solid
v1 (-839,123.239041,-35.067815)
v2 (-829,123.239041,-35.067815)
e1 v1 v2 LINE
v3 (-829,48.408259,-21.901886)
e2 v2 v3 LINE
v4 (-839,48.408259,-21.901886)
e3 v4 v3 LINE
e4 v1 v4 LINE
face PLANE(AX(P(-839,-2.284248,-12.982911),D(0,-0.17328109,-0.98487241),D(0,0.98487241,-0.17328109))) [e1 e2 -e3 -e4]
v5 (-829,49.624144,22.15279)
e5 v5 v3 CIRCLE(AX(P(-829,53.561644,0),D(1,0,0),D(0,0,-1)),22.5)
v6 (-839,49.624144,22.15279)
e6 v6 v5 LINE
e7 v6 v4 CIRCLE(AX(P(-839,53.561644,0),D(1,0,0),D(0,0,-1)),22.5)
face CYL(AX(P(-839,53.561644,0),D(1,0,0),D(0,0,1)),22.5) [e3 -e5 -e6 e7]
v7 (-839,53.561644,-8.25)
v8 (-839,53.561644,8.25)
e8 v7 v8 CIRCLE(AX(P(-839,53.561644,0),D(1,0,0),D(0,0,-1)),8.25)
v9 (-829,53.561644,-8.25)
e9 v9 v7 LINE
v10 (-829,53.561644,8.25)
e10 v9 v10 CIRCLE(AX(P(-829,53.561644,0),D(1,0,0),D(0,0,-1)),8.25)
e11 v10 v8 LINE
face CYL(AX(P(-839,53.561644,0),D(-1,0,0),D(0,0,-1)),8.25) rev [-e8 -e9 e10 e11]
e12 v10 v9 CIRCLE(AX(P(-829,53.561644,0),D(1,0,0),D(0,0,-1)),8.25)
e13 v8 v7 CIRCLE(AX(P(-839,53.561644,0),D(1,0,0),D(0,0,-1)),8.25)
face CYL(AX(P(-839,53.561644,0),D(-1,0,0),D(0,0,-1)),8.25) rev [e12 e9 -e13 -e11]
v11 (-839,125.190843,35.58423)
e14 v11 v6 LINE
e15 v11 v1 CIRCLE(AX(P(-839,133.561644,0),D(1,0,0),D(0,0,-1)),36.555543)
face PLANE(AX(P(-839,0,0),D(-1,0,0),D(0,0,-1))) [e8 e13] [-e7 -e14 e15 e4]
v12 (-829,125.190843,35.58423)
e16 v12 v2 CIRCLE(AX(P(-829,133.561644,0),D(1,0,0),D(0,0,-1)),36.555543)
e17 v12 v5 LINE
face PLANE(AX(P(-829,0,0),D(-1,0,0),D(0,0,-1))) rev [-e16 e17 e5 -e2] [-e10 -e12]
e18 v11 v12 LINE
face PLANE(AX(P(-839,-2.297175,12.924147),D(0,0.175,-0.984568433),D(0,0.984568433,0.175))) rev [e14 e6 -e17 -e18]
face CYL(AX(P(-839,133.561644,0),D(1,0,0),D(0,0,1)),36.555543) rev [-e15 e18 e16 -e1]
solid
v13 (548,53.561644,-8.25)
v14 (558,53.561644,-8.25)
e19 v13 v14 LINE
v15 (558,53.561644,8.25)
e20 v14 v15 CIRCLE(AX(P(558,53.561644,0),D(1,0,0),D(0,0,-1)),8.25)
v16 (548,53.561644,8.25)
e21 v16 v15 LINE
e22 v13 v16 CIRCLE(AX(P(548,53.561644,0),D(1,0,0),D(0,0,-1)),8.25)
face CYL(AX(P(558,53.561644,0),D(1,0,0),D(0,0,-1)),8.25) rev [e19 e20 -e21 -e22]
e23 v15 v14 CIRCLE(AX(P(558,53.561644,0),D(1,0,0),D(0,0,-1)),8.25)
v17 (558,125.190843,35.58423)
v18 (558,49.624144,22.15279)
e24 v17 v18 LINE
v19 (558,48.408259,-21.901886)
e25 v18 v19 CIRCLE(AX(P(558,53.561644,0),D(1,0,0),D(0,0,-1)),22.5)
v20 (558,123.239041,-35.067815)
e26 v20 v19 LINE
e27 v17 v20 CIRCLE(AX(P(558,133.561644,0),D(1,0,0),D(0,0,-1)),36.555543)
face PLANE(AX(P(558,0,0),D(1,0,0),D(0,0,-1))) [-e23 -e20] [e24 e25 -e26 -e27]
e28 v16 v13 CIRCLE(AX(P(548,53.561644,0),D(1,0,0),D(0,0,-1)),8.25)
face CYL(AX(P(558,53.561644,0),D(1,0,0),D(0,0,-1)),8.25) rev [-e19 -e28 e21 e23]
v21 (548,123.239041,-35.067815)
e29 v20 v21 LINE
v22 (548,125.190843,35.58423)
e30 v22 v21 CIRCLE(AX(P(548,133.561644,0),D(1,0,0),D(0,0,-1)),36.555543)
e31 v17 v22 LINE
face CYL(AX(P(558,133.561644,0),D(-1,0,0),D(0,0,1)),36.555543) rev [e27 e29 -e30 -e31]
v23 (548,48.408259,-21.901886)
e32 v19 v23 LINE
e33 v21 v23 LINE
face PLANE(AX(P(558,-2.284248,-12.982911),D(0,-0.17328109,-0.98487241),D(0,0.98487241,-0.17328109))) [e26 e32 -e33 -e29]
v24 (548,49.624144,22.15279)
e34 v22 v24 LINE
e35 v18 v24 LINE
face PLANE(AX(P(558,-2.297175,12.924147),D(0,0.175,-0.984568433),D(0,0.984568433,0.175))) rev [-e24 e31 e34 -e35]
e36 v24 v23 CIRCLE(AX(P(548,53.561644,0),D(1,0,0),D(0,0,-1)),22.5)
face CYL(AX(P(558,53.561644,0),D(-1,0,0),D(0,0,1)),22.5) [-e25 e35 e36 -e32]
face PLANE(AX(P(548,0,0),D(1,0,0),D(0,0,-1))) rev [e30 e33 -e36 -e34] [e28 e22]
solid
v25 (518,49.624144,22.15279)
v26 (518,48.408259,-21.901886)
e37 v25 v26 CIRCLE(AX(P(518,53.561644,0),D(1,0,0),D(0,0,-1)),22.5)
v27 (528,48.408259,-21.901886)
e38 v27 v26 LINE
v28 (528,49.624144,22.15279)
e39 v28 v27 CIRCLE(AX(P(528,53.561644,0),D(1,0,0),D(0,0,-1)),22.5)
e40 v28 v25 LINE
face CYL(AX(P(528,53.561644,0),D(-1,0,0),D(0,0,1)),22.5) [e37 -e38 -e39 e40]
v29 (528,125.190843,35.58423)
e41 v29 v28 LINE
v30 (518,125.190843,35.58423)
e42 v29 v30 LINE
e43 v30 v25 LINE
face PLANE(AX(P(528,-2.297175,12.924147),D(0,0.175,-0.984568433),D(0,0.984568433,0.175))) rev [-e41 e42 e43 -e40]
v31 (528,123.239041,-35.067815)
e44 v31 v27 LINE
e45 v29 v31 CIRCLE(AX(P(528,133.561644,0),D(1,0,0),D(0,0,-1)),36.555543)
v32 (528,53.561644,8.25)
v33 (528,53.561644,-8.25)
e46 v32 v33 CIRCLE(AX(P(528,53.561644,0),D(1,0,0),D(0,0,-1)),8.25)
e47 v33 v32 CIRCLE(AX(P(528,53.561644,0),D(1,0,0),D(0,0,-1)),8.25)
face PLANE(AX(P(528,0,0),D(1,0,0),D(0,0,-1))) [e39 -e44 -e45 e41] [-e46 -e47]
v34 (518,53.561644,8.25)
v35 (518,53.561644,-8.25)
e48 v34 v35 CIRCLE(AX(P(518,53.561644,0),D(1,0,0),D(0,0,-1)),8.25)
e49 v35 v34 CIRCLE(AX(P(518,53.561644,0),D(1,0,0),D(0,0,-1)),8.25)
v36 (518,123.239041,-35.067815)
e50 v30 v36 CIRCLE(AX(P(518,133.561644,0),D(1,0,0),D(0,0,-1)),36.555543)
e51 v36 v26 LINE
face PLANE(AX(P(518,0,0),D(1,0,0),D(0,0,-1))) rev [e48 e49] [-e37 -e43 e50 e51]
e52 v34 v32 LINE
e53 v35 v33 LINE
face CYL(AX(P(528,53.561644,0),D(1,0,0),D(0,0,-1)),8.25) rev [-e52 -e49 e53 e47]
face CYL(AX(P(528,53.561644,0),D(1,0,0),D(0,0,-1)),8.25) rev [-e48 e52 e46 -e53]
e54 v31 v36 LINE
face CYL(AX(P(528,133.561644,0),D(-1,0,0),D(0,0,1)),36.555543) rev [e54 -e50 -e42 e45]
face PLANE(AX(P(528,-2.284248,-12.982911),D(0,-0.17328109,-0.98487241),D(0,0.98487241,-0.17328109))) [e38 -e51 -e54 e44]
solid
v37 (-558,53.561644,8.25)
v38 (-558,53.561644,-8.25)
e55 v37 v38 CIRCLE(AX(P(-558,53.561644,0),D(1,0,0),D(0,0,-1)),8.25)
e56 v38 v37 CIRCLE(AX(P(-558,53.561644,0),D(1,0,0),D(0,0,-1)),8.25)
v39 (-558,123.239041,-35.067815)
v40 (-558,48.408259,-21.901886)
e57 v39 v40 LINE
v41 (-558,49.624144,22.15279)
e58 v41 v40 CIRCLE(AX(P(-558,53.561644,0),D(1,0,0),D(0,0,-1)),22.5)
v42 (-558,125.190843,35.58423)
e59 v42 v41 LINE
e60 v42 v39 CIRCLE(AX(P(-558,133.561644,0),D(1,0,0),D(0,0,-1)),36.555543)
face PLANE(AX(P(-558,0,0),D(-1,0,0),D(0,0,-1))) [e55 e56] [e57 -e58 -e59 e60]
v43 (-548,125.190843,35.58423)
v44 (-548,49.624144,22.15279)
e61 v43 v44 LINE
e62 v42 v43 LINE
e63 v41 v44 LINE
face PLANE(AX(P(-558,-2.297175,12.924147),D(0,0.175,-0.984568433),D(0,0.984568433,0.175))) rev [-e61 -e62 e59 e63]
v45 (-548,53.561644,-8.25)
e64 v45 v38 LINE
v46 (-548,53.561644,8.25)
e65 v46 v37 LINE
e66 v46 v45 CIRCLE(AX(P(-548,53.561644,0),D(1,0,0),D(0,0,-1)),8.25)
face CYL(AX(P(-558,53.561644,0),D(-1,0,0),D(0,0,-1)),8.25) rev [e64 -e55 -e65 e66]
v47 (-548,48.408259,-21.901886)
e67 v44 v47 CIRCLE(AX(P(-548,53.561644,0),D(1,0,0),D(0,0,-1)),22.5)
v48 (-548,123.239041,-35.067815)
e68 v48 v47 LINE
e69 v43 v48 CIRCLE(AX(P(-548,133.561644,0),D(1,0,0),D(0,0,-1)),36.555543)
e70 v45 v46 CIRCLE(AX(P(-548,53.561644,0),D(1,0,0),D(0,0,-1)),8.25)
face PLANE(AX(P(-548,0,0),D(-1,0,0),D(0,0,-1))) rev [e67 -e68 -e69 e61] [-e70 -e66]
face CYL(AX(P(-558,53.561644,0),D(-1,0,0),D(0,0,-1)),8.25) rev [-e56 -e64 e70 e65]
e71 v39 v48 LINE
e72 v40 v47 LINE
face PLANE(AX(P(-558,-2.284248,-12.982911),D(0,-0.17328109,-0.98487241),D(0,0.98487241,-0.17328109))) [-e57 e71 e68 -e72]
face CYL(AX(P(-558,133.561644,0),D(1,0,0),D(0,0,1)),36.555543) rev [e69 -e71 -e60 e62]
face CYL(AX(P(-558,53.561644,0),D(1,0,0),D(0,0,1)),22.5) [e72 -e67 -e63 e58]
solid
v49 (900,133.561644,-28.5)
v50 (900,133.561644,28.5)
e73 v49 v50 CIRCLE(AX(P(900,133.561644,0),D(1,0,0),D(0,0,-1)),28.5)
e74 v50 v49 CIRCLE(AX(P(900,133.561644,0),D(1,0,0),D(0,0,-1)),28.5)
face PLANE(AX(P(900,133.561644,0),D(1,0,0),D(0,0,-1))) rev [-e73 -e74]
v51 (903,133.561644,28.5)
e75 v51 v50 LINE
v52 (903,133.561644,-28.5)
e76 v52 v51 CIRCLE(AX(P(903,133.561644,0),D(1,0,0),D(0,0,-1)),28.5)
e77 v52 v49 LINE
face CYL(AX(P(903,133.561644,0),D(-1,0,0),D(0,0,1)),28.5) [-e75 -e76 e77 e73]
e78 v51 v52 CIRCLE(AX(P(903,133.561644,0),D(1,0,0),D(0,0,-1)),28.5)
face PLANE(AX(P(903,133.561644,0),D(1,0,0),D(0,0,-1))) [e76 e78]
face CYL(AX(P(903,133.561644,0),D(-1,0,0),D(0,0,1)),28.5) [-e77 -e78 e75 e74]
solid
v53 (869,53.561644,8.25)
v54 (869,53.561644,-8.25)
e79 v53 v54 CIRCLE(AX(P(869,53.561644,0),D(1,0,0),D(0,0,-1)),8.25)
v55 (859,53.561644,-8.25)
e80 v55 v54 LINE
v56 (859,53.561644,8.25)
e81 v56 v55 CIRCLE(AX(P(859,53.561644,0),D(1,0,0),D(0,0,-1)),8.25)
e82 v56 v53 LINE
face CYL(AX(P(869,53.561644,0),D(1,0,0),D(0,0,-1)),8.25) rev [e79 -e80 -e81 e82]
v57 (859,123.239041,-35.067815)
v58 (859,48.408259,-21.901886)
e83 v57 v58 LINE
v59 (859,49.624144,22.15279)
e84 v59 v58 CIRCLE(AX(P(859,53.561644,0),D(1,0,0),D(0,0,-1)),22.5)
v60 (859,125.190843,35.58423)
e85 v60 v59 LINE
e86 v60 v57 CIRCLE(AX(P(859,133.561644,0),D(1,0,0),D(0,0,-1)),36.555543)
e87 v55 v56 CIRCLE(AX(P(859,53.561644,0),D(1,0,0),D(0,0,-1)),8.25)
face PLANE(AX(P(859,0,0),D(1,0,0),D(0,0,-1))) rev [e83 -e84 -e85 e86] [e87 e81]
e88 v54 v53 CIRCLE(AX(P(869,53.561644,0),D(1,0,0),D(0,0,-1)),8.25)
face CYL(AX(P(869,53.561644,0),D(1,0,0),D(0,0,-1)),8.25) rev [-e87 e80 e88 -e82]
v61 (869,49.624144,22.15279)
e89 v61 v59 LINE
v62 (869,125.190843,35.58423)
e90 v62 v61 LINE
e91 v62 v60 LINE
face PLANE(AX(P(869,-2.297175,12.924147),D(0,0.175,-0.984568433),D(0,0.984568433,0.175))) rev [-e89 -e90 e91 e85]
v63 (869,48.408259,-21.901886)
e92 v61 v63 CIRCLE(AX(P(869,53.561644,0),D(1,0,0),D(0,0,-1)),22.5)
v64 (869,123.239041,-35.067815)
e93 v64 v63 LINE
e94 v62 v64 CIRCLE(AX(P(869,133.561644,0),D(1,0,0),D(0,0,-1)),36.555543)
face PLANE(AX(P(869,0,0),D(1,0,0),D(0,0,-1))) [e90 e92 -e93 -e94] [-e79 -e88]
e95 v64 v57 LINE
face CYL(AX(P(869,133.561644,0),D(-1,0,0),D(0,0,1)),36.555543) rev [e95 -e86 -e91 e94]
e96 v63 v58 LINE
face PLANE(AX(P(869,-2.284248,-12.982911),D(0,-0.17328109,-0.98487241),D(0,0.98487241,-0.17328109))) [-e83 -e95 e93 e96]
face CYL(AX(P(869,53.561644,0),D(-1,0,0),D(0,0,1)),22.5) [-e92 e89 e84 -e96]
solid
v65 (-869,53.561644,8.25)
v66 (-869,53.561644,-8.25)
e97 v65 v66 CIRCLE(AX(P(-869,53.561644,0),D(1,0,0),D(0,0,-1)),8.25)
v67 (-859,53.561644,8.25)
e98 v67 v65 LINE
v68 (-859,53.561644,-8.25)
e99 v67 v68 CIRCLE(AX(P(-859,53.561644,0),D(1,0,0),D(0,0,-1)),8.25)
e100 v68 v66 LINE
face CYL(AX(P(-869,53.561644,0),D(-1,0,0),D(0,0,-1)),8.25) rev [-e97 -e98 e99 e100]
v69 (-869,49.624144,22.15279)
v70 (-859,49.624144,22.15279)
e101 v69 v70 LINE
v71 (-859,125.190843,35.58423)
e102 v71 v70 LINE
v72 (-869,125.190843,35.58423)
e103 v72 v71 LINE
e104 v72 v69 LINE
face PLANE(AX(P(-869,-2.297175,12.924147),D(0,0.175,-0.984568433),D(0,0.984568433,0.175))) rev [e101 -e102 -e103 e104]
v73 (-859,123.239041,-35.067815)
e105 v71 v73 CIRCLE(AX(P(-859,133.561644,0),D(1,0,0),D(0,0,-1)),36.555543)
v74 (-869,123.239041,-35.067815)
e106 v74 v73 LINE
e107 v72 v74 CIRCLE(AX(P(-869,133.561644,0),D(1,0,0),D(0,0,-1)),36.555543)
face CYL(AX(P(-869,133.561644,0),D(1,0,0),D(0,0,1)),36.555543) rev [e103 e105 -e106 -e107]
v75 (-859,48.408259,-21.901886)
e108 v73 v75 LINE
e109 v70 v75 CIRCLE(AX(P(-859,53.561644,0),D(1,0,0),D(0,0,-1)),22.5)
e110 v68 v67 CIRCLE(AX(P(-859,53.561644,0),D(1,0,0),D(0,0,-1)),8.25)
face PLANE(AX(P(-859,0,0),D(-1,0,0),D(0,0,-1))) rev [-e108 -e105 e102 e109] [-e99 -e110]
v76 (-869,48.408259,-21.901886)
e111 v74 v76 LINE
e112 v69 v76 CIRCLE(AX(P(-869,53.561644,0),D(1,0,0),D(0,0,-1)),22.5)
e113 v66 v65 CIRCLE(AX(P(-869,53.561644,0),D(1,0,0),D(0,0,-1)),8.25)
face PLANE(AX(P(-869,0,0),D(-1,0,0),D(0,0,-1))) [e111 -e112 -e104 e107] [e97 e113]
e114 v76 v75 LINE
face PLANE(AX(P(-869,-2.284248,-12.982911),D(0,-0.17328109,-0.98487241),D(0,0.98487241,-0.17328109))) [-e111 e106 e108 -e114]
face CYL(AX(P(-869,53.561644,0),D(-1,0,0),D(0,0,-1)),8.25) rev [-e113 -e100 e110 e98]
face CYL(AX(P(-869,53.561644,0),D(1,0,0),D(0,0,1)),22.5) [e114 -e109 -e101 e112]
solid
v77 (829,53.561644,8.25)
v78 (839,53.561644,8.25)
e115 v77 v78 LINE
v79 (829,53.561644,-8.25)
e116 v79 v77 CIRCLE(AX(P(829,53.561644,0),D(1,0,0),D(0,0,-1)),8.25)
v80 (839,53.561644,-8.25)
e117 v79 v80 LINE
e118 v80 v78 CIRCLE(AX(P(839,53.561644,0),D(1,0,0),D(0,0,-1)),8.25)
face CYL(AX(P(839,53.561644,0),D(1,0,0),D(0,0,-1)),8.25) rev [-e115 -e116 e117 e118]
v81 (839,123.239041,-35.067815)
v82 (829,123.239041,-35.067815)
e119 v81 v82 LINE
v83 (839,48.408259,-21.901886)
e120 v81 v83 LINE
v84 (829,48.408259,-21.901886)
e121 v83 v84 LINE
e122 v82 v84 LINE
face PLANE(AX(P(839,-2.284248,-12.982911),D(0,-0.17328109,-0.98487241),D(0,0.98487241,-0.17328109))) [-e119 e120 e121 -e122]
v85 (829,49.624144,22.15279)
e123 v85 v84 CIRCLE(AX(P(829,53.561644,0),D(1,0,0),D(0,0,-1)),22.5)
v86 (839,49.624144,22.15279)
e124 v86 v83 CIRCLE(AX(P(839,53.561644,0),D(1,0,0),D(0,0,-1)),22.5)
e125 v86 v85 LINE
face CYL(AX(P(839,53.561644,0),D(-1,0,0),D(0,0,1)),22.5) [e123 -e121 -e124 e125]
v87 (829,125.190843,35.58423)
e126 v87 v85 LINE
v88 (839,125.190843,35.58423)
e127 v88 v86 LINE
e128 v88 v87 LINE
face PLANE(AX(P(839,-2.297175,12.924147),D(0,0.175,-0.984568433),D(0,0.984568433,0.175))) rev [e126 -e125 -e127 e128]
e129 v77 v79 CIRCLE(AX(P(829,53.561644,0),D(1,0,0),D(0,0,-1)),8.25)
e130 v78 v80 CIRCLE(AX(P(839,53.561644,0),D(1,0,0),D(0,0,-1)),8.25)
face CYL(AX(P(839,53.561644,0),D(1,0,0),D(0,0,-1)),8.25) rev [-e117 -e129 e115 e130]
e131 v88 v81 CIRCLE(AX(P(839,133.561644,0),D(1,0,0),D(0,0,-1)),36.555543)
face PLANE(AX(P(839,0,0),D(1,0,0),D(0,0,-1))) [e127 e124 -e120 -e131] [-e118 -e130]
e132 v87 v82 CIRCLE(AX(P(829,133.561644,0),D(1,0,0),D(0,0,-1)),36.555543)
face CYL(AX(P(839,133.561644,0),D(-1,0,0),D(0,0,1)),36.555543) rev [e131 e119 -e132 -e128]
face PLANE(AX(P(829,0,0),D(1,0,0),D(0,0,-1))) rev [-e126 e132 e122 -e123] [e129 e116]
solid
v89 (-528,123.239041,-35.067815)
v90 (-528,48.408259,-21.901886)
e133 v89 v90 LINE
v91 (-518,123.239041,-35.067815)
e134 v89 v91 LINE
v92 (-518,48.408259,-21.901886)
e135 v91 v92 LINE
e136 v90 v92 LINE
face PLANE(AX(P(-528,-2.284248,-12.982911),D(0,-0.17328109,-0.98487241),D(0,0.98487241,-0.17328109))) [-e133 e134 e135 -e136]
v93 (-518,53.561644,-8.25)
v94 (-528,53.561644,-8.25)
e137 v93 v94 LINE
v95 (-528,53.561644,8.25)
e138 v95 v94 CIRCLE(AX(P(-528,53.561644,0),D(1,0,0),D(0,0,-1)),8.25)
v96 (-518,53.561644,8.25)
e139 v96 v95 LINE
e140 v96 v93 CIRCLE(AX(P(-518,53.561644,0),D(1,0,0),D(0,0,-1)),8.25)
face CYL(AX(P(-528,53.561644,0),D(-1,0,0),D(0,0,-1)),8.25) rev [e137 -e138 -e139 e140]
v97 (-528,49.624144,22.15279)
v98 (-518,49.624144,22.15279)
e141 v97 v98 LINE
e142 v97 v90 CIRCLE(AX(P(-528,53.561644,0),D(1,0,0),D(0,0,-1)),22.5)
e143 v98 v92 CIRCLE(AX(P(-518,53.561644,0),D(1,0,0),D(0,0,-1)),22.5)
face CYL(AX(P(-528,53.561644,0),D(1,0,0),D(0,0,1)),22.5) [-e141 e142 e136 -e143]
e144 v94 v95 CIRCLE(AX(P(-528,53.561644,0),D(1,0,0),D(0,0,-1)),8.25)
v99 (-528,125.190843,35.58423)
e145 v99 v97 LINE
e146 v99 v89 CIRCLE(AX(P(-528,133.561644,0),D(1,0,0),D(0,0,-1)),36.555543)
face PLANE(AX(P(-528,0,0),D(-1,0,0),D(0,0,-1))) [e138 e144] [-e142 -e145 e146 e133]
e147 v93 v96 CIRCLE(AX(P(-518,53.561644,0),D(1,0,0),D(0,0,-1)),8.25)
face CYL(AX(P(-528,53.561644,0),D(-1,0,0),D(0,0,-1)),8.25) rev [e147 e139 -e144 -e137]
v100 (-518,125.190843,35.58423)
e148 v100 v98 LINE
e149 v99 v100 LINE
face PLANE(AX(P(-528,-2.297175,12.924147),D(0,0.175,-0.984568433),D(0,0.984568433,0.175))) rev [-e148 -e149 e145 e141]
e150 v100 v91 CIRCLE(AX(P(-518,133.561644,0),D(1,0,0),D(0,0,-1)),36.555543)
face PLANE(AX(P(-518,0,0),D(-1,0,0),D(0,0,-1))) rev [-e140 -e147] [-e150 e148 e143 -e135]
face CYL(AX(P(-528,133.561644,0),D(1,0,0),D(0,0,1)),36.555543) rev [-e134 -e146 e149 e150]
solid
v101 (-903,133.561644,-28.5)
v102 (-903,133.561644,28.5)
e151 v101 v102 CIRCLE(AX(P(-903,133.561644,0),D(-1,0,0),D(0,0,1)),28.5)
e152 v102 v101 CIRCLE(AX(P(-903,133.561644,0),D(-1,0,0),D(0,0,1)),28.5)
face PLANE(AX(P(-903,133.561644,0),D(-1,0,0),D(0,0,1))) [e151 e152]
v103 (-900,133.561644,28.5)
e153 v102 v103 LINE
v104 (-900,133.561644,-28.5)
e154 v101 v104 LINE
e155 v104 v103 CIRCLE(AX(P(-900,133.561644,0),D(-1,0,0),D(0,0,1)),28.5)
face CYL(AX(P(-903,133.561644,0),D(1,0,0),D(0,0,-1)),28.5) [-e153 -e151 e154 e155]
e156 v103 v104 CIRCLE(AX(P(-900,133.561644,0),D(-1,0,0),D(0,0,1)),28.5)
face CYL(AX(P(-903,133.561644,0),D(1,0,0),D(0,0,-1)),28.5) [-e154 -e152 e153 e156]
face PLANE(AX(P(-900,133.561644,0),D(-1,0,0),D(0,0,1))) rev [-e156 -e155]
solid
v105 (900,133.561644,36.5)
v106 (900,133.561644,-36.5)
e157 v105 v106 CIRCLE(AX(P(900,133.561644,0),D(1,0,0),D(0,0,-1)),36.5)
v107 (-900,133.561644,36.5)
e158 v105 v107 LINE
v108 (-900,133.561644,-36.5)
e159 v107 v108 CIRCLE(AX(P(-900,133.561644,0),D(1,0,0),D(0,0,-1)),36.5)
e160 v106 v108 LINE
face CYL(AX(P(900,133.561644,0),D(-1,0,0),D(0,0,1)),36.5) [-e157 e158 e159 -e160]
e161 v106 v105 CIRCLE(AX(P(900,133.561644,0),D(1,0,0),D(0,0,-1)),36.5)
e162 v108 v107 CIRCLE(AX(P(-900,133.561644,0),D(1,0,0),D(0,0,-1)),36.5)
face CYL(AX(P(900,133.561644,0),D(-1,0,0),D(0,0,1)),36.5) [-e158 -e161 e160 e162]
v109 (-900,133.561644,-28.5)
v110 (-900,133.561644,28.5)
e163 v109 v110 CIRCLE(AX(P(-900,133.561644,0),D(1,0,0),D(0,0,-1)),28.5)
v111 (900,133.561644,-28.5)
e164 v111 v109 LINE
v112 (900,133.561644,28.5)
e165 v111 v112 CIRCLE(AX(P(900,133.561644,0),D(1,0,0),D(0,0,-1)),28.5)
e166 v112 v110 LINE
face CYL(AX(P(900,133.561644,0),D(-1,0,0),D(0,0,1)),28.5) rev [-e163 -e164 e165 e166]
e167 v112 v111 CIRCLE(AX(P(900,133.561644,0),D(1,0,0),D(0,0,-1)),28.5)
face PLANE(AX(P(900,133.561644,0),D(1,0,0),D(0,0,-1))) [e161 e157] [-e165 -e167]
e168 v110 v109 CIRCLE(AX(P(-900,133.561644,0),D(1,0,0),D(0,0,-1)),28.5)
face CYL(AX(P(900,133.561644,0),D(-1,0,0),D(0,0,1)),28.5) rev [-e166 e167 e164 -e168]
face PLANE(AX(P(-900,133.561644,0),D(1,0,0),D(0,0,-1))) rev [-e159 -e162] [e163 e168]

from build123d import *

# Parameters (mm, degrees)
SKETCH1_R                = 36.5
SKETCH1_R_2              = 28.5
STRUCTURAL_MEMBER1_DEPTH = 1800
BOSS_EXTRUDE1_START      = 10
BOSS_EXTRUDE1_DEPTH      = 10
SKETCH4_W                = 8.25
SKETCH4_H                = 10.001
LPATTERN1_COUNT          = 2
LPATTERN1_PITCH          = 30
LPATTERN2_COUNT          = 2
LPATTERN2_PITCH          = 311
SKETCH7_R                = 28.5
BOSS_EXTRUDE2_DEPTH      = 3
SKETCH8_R                = 28.5
BOSS_EXTRUDE3_DEPTH      = 3


with BuildPart() as part:
    # Sketch1 → Structural Member1 (new body)
    with BuildSketch(Plane(origin=(-900, 133.561643836, 0), x_dir=(0, 1, 0), z_dir=(1, 0, 0))):
        Circle(SKETCH1_R)
        Circle(SKETCH1_R_2, mode=Mode.SUBTRACT)
    extrude(amount=STRUCTURAL_MEMBER1_DEPTH)


with BuildPart() as body_2:
    # Sketch3 → Boss-Extrude1 (new body)
    with BuildSketch(Plane(origin=(538, 0, 0), x_dir=(0, 0, -1), z_dir=(1, 0, 0)).offset(BOSS_EXTRUDE1_START)):
        with BuildLine():
            ThreePointArc((35.067814515, 123.239040731), (-1.009482351, 97.020041585), (-35.584230323, 125.190843277))
            Line((-35.584230323, 125.190843277), (-22.152789751, 49.624143836))
            ThreePointArc((-22.152789751, 49.624143836), (-0.62075134, 31.070208404), (21.901886288, 48.408258827))
            Line((21.901886288, 48.408258827), (35.067814515, 123.239040731))
        make_face()
    extrude(amount=BOSS_EXTRUDE1_DEPTH)

    # Sketch4 → Ø16.5 (16.5) Diameter Hole1 (revolve, cut)
    with BuildSketch(Plane(origin=(558, 53.561643836, 0), x_dir=(0, 0, -1), z_dir=(0, 1, 0))):
        with Locations((4.125, 5.0005)):
            Rectangle(SKETCH4_W, SKETCH4_H)
    revolve(axis=Axis((564.35, 53.561643836, 0), (-1, 0, 0)), mode=Mode.SUBTRACT)


with BuildPart() as lpattern1_1:
    # LPattern1: pattern copy
    add(body_2.part.moved(Location(Vector(-1, 0, 0) * (1 * LPATTERN1_PITCH))))


with BuildPart() as body_4:
    # Mirror1: mirrored copy
    add(lpattern1_1.part.mirror(Plane(origin=(0, 0, 0), x_dir=(0, 0, 1), z_dir=(1, 0, 0))))


with BuildPart() as body_5:
    # Mirror1 2: mirrored copy
    add(body_2.part.mirror(Plane(origin=(0, 0, 0), x_dir=(0, 0, 1), z_dir=(1, 0, 0))))


with BuildPart() as lpattern2_1:
    # LPattern2: pattern copy
    add(lpattern1_1.part.moved(Location(Vector(1, 0, 0) * (1 * LPATTERN2_PITCH))))


with BuildPart() as lpattern2_2:
    # LPattern2: pattern copy
    add(body_2.part.moved(Location(Vector(1, 0, 0) * (1 * LPATTERN2_PITCH))))


with BuildPart() as body_8:
    # Mirror2: mirrored copy
    add(lpattern2_1.part.mirror(Plane(origin=(0, 0, 0), x_dir=(0, 0, 1), z_dir=(1, 0, 0))))


with BuildPart() as body_9:
    # Mirror2 2: mirrored copy
    add(lpattern2_2.part.mirror(Plane(origin=(0, 0, 0), x_dir=(0, 0, 1), z_dir=(1, 0, 0))))


with BuildPart() as body_10:
    # Sketch7 → Boss-Extrude2 (new body)
    with BuildSketch(Plane.ZY.offset(900)):
        with Locations((0, 133.561643836)):
            Circle(SKETCH7_R)
    extrude(amount=BOSS_EXTRUDE2_DEPTH)


with BuildPart() as body_11:
    # Sketch8 → Boss-Extrude3 (new body)
    with BuildSketch(Plane(origin=(900, 0, 0), x_dir=(0, 0, -1), z_dir=(1, 0, 0))):
        with Locations((0, 133.561643836)):
            Circle(SKETCH8_R)
    extrude(amount=BOSS_EXTRUDE3_DEPTH)


solid = Compound([part.part, body_2.part, lpattern1_1.part, body_4.part, body_5.part, lpattern2_1.part, lpattern2_2.part, body_8.part, body_9.part, body_10.part, body_11.part])
